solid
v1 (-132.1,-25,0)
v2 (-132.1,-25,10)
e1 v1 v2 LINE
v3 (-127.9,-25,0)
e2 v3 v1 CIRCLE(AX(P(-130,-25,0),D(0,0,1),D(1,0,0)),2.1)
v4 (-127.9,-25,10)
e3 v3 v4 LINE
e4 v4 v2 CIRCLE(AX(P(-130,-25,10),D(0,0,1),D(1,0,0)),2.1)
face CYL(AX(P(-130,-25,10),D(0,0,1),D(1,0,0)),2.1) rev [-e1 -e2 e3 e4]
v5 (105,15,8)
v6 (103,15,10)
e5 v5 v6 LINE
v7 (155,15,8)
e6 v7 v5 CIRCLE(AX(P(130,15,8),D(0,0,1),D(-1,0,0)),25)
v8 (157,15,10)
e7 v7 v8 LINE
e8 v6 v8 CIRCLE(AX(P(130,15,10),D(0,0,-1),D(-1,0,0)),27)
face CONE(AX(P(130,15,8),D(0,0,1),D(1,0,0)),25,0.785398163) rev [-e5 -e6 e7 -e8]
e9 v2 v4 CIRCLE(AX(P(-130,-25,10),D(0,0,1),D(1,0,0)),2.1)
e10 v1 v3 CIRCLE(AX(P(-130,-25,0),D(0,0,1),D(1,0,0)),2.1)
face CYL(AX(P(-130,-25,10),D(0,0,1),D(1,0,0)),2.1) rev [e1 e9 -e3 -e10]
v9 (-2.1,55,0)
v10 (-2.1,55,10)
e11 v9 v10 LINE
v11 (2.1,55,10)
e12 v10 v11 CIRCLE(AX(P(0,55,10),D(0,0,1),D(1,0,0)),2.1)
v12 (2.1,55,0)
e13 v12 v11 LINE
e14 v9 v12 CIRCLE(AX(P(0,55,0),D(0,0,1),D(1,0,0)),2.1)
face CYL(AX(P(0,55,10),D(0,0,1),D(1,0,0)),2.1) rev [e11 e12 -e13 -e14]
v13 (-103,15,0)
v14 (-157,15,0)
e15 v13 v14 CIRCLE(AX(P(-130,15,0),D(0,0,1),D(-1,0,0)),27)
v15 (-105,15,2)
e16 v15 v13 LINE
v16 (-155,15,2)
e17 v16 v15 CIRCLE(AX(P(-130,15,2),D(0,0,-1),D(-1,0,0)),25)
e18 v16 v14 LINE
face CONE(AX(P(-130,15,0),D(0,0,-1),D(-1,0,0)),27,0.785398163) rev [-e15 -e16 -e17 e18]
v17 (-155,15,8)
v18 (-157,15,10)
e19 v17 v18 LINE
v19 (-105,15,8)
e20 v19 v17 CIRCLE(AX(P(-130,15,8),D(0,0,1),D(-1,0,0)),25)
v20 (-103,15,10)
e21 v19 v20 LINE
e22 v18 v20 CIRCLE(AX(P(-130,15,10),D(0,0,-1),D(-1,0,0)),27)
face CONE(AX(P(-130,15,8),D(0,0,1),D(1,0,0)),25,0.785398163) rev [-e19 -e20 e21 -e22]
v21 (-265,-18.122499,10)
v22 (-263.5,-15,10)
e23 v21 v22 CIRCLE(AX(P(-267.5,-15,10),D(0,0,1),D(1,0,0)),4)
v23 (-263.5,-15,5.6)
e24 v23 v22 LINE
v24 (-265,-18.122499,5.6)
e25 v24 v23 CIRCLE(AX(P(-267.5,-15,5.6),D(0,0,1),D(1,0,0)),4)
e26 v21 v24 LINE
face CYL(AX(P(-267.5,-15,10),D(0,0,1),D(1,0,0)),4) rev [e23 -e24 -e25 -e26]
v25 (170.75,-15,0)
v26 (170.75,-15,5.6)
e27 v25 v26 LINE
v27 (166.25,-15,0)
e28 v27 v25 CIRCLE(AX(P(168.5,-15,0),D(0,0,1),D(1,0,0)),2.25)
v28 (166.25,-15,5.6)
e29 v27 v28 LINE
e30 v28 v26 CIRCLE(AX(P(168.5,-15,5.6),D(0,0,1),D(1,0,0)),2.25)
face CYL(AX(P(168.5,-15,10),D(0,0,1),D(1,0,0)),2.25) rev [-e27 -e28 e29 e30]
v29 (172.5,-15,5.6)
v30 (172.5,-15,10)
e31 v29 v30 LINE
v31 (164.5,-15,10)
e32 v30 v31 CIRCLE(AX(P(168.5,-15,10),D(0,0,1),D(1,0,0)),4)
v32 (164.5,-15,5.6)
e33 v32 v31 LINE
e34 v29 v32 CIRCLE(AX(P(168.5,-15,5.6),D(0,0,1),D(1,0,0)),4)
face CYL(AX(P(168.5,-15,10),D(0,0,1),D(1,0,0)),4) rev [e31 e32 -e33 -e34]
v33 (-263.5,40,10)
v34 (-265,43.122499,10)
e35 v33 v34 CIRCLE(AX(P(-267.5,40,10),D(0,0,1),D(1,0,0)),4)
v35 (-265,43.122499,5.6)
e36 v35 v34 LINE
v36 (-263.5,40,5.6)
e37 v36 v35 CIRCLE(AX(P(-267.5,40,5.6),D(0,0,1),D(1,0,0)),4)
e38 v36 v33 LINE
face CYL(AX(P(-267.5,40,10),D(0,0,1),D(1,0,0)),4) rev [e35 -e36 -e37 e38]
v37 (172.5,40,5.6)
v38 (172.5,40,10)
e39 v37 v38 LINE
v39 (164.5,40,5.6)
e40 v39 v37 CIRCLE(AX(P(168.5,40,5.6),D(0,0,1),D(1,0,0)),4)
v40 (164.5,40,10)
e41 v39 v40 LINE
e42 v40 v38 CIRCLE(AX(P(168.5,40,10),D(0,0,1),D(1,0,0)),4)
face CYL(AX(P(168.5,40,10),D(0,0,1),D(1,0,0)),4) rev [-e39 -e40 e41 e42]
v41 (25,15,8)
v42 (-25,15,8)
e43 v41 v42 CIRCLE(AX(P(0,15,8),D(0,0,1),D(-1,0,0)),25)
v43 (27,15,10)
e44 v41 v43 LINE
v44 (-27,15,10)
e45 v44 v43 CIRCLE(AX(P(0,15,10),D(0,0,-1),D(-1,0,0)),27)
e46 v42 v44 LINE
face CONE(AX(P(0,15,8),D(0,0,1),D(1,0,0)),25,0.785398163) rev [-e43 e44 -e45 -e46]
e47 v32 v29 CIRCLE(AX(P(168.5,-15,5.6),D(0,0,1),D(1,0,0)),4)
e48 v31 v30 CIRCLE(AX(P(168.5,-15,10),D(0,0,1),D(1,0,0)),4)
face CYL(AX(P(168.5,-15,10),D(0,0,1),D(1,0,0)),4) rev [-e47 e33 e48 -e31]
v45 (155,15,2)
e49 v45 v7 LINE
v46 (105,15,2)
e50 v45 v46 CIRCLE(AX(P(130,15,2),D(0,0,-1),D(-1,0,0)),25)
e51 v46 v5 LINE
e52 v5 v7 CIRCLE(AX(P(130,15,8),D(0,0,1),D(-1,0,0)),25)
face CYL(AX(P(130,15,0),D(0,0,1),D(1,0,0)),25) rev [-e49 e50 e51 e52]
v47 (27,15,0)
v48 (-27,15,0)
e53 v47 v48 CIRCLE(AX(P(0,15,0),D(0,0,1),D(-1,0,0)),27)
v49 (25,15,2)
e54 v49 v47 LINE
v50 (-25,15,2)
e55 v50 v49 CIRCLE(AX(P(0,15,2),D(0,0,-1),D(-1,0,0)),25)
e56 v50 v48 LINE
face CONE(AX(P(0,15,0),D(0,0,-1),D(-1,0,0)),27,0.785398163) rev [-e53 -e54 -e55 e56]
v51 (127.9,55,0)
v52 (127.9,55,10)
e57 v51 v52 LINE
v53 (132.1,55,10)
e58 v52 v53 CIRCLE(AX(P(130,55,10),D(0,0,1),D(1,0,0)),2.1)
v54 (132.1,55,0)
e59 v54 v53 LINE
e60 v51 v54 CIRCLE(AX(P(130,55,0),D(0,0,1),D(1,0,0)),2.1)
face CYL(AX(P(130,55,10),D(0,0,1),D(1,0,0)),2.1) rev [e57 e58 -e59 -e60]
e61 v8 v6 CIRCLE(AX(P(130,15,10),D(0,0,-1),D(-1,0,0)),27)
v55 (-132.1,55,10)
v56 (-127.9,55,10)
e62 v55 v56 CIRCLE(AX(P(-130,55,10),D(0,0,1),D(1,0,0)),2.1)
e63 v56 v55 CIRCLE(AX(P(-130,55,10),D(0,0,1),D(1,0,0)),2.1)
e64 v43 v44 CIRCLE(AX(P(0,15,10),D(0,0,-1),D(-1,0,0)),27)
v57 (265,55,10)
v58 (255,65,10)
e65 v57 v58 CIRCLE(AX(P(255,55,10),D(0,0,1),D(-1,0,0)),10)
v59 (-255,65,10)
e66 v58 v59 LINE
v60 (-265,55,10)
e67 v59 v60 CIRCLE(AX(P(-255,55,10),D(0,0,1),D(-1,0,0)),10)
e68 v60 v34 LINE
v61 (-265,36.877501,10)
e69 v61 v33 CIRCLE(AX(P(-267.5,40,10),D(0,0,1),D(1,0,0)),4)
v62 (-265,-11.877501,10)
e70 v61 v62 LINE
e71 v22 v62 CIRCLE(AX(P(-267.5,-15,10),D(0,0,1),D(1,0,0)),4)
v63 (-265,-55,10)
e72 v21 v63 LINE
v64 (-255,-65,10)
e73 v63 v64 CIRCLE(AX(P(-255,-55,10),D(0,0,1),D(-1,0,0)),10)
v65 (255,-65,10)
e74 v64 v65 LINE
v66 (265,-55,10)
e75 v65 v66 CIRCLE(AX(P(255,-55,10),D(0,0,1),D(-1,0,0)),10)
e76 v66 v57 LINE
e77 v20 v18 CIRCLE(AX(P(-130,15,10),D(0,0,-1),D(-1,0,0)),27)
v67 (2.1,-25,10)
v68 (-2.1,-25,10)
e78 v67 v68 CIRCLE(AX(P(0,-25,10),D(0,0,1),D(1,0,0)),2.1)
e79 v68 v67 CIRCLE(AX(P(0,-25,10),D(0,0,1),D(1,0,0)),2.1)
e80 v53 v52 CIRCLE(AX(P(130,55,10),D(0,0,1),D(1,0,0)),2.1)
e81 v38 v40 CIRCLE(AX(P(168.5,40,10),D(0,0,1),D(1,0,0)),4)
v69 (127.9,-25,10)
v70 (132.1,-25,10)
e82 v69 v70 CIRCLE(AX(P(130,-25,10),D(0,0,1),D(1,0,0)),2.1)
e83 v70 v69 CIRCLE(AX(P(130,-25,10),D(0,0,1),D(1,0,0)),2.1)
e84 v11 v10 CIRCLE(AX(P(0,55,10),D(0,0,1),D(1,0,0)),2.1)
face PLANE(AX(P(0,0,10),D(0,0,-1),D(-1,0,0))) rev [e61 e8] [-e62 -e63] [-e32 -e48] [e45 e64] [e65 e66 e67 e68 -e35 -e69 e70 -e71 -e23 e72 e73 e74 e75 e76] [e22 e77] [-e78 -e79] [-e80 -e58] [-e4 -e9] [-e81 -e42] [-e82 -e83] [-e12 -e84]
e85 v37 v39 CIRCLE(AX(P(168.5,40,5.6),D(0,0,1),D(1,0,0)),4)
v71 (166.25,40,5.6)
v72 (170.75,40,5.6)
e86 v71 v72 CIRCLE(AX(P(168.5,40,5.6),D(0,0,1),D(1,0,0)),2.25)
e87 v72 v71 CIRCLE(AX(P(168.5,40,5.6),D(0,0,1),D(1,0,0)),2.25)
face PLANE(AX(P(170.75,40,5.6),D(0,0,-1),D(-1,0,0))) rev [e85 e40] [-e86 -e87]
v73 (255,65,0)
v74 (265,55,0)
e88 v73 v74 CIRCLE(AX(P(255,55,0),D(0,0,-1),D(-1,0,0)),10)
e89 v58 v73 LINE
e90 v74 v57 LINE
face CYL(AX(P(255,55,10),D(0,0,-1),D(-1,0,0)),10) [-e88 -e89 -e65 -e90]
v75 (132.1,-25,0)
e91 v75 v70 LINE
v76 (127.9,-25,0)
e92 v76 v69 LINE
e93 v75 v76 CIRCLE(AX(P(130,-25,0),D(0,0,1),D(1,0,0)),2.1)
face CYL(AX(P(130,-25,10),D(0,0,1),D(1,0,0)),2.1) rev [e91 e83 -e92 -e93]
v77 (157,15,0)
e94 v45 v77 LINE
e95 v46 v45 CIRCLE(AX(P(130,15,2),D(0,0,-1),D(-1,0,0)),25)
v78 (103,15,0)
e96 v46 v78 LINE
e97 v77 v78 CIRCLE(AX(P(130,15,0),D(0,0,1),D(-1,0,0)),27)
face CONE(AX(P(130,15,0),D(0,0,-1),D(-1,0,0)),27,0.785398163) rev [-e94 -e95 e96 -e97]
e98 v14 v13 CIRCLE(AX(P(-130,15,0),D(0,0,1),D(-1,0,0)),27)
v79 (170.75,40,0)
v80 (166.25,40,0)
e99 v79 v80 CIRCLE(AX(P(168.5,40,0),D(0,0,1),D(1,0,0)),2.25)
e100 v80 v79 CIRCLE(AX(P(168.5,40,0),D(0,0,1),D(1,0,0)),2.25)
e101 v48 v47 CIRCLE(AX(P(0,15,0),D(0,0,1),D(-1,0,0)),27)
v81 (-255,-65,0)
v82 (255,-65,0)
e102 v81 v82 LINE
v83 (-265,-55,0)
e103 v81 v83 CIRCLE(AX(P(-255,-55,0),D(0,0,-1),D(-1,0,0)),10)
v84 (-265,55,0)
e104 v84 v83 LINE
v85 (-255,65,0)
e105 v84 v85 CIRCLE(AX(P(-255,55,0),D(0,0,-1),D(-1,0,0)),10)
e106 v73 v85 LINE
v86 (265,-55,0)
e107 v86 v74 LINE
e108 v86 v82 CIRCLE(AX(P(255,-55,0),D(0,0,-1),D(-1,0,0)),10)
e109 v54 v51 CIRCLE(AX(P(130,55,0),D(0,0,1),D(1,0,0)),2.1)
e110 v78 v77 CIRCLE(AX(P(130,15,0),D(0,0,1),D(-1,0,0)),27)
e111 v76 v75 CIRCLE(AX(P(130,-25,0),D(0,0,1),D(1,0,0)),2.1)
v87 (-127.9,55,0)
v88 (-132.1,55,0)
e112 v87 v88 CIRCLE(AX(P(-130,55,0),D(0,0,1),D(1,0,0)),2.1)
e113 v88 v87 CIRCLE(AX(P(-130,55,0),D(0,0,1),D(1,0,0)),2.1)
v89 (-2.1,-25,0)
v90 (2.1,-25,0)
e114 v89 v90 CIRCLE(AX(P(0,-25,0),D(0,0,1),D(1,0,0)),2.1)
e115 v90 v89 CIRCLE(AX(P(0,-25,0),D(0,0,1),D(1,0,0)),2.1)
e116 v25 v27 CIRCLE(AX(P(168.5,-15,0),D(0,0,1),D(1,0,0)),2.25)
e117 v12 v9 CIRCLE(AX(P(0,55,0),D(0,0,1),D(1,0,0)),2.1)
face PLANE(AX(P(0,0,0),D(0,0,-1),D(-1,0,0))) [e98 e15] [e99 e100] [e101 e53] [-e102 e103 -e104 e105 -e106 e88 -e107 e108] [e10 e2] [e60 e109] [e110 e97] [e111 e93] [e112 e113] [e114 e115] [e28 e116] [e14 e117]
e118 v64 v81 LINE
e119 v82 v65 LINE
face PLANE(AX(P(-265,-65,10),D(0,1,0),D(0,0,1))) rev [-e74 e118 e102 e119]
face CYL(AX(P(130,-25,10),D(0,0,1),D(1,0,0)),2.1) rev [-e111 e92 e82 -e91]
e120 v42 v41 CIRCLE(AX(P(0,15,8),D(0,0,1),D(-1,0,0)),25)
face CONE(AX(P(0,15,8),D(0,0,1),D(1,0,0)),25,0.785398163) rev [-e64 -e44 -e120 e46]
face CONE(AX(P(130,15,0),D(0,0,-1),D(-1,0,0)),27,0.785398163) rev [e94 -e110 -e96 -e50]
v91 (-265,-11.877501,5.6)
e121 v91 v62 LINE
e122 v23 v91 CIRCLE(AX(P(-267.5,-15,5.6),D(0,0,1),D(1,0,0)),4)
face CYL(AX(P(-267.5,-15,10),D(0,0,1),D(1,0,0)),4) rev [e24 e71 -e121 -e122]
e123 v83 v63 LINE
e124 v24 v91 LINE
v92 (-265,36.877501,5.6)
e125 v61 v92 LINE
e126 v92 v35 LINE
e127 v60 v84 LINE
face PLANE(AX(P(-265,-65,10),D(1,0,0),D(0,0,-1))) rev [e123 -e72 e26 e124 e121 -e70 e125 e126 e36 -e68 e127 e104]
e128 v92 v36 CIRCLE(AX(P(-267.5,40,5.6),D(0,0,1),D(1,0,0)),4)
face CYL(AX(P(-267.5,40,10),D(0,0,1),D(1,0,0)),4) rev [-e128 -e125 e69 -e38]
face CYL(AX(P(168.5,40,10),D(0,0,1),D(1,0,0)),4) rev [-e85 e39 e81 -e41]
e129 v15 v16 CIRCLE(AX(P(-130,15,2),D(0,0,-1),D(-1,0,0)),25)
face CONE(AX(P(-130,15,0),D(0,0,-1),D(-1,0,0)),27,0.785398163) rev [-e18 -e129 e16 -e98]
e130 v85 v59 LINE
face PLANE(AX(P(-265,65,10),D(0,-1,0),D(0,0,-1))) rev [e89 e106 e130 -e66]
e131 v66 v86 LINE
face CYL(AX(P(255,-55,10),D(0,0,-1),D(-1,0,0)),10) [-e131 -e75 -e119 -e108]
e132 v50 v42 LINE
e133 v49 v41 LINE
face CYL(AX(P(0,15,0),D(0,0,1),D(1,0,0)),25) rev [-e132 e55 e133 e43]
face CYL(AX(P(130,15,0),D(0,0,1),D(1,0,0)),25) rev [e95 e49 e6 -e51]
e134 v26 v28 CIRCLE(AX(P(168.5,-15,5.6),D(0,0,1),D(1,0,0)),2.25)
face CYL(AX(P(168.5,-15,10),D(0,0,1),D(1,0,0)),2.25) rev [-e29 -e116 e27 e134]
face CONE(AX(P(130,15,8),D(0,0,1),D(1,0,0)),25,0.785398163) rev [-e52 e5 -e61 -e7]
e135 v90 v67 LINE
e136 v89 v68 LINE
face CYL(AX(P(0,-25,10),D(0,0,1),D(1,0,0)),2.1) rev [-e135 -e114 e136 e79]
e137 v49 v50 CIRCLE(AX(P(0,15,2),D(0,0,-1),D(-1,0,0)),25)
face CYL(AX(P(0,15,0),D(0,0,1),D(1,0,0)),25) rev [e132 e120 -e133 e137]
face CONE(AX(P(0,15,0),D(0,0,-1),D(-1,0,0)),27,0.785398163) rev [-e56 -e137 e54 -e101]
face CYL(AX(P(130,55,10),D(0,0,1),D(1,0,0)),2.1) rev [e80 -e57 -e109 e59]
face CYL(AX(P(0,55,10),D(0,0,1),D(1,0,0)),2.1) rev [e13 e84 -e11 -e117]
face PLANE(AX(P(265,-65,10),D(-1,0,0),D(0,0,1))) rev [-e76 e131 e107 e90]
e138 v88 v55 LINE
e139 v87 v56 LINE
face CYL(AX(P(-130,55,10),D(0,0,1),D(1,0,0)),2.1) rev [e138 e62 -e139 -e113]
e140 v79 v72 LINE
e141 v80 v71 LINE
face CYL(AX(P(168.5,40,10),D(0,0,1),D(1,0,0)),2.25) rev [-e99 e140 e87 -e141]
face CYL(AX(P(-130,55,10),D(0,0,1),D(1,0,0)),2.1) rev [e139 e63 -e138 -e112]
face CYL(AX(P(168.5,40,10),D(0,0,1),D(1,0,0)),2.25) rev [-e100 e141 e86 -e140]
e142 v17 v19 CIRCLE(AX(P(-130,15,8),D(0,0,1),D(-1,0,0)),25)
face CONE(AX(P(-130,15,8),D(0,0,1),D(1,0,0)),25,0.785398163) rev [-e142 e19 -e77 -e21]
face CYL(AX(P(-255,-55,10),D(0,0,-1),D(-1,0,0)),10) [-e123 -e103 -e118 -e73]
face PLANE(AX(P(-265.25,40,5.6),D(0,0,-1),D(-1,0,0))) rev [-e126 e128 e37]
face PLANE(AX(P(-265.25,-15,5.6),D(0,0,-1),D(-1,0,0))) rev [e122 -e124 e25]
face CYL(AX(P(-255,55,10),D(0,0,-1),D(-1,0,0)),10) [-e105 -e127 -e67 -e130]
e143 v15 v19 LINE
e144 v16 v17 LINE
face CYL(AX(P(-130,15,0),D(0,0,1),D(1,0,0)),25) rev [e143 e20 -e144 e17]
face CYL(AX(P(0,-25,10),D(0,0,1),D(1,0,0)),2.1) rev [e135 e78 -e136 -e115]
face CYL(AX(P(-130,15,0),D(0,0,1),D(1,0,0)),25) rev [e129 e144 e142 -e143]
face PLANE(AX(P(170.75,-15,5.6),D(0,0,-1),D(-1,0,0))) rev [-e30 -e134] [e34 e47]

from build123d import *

# Parameters (mm, degrees)
SKETCH_1_W                   = 530
SKETCH_1_H                   = 130
EXTRUDE_1_DEPTH              = 10
HOLE_WIZARD_M4_1_D           = 4.5
HOLE_WIZARD_M4_1_CBORE_D     = 8
HOLE_WIZARD_M4_1_CBORE_DEPTH = 4.4
PATTERN_LINEAR_1_COUNT       = 2
PATTERN_LINEAR_1_PITCH       = 436
SKETCH_14_R                  = 25
CUT_EXTRUDE_1_DEPTH          = 274.03845883
CHAMFER_1_SIZE               = 2
HOLE_WIZARD_M5_2_D           = 4.2
FILLET_1_R                   = 10


with BuildPart() as part:
    # 草图1 → 凸台-拉伸1 (new body)
    with BuildSketch(Plane.XY):
        Rectangle(SKETCH_1_W, SKETCH_1_H)
    extrude(amount=EXTRUDE_1_DEPTH)

    # M4 六角凹头螺钉的柱形沉头孔1 (through all)
    with Locations(Plane(origin=(0, 0, 10), x_dir=(-1, 0, 0), z_dir=(0, 0, 1))):
        with Locations((-168.5, 15), (-168.5, -40)):
            hole_wizard_m4_1 = CounterBoreHole(HOLE_WIZARD_M4_1_D / 2, HOLE_WIZARD_M4_1_CBORE_D / 2, HOLE_WIZARD_M4_1_CBORE_DEPTH)

    # 阵列(线性)1: M4 六角凹头螺钉的柱形沉头孔1 ×2
    with Locations(*[(-i * PATTERN_LINEAR_1_PITCH, 0, 0) for i in range(1, PATTERN_LINEAR_1_COUNT)]):
        add(hole_wizard_m4_1, mode=Mode.SUBTRACT)

    # 草图14 → 切除-拉伸1 (cut, through all)
    with BuildSketch(Plane.XY.offset(10)):
        with Locations((-130, 15)):
            Circle(SKETCH_14_R)
        with Locations((0, 15)):
            Circle(SKETCH_14_R)
        with Locations((130, 15)):
            Circle(SKETCH_14_R)
    extrude(amount=-CUT_EXTRUDE_1_DEPTH, mode=Mode.SUBTRACT)

    # 倒角1
    chamfer_1_edges = [part.edges().sort_by_distance(p)[0] for p in [
        (-155, 15, 0),
        (-155, 15, 10),
        (-25, 15, 0),
        (-25, 15, 10),
        (105, 15, 0),
        (105, 15, 10),
    ]]
    chamfer(chamfer_1_edges, length=CHAMFER_1_SIZE)

    # M5 螺纹孔2 (through all)
    with Locations(Plane.XY.offset(10)):
        with Locations((130, 55), (-130, -25), (-130, 55), (0, 55), (0, -25), (130, -25)):
            Hole(HOLE_WIZARD_M5_2_D / 2)

    # 圆角1
    fillet_1_edges = [part.edges().sort_by_distance(p)[0] for p in [
        (265, -65, 5),
        (-265, -65, 5),
        (-265, 65, 5),
        (265, 65, 5),
    ]]
    fillet(fillet_1_edges, radius=FILLET_1_R)


solid = part.part
